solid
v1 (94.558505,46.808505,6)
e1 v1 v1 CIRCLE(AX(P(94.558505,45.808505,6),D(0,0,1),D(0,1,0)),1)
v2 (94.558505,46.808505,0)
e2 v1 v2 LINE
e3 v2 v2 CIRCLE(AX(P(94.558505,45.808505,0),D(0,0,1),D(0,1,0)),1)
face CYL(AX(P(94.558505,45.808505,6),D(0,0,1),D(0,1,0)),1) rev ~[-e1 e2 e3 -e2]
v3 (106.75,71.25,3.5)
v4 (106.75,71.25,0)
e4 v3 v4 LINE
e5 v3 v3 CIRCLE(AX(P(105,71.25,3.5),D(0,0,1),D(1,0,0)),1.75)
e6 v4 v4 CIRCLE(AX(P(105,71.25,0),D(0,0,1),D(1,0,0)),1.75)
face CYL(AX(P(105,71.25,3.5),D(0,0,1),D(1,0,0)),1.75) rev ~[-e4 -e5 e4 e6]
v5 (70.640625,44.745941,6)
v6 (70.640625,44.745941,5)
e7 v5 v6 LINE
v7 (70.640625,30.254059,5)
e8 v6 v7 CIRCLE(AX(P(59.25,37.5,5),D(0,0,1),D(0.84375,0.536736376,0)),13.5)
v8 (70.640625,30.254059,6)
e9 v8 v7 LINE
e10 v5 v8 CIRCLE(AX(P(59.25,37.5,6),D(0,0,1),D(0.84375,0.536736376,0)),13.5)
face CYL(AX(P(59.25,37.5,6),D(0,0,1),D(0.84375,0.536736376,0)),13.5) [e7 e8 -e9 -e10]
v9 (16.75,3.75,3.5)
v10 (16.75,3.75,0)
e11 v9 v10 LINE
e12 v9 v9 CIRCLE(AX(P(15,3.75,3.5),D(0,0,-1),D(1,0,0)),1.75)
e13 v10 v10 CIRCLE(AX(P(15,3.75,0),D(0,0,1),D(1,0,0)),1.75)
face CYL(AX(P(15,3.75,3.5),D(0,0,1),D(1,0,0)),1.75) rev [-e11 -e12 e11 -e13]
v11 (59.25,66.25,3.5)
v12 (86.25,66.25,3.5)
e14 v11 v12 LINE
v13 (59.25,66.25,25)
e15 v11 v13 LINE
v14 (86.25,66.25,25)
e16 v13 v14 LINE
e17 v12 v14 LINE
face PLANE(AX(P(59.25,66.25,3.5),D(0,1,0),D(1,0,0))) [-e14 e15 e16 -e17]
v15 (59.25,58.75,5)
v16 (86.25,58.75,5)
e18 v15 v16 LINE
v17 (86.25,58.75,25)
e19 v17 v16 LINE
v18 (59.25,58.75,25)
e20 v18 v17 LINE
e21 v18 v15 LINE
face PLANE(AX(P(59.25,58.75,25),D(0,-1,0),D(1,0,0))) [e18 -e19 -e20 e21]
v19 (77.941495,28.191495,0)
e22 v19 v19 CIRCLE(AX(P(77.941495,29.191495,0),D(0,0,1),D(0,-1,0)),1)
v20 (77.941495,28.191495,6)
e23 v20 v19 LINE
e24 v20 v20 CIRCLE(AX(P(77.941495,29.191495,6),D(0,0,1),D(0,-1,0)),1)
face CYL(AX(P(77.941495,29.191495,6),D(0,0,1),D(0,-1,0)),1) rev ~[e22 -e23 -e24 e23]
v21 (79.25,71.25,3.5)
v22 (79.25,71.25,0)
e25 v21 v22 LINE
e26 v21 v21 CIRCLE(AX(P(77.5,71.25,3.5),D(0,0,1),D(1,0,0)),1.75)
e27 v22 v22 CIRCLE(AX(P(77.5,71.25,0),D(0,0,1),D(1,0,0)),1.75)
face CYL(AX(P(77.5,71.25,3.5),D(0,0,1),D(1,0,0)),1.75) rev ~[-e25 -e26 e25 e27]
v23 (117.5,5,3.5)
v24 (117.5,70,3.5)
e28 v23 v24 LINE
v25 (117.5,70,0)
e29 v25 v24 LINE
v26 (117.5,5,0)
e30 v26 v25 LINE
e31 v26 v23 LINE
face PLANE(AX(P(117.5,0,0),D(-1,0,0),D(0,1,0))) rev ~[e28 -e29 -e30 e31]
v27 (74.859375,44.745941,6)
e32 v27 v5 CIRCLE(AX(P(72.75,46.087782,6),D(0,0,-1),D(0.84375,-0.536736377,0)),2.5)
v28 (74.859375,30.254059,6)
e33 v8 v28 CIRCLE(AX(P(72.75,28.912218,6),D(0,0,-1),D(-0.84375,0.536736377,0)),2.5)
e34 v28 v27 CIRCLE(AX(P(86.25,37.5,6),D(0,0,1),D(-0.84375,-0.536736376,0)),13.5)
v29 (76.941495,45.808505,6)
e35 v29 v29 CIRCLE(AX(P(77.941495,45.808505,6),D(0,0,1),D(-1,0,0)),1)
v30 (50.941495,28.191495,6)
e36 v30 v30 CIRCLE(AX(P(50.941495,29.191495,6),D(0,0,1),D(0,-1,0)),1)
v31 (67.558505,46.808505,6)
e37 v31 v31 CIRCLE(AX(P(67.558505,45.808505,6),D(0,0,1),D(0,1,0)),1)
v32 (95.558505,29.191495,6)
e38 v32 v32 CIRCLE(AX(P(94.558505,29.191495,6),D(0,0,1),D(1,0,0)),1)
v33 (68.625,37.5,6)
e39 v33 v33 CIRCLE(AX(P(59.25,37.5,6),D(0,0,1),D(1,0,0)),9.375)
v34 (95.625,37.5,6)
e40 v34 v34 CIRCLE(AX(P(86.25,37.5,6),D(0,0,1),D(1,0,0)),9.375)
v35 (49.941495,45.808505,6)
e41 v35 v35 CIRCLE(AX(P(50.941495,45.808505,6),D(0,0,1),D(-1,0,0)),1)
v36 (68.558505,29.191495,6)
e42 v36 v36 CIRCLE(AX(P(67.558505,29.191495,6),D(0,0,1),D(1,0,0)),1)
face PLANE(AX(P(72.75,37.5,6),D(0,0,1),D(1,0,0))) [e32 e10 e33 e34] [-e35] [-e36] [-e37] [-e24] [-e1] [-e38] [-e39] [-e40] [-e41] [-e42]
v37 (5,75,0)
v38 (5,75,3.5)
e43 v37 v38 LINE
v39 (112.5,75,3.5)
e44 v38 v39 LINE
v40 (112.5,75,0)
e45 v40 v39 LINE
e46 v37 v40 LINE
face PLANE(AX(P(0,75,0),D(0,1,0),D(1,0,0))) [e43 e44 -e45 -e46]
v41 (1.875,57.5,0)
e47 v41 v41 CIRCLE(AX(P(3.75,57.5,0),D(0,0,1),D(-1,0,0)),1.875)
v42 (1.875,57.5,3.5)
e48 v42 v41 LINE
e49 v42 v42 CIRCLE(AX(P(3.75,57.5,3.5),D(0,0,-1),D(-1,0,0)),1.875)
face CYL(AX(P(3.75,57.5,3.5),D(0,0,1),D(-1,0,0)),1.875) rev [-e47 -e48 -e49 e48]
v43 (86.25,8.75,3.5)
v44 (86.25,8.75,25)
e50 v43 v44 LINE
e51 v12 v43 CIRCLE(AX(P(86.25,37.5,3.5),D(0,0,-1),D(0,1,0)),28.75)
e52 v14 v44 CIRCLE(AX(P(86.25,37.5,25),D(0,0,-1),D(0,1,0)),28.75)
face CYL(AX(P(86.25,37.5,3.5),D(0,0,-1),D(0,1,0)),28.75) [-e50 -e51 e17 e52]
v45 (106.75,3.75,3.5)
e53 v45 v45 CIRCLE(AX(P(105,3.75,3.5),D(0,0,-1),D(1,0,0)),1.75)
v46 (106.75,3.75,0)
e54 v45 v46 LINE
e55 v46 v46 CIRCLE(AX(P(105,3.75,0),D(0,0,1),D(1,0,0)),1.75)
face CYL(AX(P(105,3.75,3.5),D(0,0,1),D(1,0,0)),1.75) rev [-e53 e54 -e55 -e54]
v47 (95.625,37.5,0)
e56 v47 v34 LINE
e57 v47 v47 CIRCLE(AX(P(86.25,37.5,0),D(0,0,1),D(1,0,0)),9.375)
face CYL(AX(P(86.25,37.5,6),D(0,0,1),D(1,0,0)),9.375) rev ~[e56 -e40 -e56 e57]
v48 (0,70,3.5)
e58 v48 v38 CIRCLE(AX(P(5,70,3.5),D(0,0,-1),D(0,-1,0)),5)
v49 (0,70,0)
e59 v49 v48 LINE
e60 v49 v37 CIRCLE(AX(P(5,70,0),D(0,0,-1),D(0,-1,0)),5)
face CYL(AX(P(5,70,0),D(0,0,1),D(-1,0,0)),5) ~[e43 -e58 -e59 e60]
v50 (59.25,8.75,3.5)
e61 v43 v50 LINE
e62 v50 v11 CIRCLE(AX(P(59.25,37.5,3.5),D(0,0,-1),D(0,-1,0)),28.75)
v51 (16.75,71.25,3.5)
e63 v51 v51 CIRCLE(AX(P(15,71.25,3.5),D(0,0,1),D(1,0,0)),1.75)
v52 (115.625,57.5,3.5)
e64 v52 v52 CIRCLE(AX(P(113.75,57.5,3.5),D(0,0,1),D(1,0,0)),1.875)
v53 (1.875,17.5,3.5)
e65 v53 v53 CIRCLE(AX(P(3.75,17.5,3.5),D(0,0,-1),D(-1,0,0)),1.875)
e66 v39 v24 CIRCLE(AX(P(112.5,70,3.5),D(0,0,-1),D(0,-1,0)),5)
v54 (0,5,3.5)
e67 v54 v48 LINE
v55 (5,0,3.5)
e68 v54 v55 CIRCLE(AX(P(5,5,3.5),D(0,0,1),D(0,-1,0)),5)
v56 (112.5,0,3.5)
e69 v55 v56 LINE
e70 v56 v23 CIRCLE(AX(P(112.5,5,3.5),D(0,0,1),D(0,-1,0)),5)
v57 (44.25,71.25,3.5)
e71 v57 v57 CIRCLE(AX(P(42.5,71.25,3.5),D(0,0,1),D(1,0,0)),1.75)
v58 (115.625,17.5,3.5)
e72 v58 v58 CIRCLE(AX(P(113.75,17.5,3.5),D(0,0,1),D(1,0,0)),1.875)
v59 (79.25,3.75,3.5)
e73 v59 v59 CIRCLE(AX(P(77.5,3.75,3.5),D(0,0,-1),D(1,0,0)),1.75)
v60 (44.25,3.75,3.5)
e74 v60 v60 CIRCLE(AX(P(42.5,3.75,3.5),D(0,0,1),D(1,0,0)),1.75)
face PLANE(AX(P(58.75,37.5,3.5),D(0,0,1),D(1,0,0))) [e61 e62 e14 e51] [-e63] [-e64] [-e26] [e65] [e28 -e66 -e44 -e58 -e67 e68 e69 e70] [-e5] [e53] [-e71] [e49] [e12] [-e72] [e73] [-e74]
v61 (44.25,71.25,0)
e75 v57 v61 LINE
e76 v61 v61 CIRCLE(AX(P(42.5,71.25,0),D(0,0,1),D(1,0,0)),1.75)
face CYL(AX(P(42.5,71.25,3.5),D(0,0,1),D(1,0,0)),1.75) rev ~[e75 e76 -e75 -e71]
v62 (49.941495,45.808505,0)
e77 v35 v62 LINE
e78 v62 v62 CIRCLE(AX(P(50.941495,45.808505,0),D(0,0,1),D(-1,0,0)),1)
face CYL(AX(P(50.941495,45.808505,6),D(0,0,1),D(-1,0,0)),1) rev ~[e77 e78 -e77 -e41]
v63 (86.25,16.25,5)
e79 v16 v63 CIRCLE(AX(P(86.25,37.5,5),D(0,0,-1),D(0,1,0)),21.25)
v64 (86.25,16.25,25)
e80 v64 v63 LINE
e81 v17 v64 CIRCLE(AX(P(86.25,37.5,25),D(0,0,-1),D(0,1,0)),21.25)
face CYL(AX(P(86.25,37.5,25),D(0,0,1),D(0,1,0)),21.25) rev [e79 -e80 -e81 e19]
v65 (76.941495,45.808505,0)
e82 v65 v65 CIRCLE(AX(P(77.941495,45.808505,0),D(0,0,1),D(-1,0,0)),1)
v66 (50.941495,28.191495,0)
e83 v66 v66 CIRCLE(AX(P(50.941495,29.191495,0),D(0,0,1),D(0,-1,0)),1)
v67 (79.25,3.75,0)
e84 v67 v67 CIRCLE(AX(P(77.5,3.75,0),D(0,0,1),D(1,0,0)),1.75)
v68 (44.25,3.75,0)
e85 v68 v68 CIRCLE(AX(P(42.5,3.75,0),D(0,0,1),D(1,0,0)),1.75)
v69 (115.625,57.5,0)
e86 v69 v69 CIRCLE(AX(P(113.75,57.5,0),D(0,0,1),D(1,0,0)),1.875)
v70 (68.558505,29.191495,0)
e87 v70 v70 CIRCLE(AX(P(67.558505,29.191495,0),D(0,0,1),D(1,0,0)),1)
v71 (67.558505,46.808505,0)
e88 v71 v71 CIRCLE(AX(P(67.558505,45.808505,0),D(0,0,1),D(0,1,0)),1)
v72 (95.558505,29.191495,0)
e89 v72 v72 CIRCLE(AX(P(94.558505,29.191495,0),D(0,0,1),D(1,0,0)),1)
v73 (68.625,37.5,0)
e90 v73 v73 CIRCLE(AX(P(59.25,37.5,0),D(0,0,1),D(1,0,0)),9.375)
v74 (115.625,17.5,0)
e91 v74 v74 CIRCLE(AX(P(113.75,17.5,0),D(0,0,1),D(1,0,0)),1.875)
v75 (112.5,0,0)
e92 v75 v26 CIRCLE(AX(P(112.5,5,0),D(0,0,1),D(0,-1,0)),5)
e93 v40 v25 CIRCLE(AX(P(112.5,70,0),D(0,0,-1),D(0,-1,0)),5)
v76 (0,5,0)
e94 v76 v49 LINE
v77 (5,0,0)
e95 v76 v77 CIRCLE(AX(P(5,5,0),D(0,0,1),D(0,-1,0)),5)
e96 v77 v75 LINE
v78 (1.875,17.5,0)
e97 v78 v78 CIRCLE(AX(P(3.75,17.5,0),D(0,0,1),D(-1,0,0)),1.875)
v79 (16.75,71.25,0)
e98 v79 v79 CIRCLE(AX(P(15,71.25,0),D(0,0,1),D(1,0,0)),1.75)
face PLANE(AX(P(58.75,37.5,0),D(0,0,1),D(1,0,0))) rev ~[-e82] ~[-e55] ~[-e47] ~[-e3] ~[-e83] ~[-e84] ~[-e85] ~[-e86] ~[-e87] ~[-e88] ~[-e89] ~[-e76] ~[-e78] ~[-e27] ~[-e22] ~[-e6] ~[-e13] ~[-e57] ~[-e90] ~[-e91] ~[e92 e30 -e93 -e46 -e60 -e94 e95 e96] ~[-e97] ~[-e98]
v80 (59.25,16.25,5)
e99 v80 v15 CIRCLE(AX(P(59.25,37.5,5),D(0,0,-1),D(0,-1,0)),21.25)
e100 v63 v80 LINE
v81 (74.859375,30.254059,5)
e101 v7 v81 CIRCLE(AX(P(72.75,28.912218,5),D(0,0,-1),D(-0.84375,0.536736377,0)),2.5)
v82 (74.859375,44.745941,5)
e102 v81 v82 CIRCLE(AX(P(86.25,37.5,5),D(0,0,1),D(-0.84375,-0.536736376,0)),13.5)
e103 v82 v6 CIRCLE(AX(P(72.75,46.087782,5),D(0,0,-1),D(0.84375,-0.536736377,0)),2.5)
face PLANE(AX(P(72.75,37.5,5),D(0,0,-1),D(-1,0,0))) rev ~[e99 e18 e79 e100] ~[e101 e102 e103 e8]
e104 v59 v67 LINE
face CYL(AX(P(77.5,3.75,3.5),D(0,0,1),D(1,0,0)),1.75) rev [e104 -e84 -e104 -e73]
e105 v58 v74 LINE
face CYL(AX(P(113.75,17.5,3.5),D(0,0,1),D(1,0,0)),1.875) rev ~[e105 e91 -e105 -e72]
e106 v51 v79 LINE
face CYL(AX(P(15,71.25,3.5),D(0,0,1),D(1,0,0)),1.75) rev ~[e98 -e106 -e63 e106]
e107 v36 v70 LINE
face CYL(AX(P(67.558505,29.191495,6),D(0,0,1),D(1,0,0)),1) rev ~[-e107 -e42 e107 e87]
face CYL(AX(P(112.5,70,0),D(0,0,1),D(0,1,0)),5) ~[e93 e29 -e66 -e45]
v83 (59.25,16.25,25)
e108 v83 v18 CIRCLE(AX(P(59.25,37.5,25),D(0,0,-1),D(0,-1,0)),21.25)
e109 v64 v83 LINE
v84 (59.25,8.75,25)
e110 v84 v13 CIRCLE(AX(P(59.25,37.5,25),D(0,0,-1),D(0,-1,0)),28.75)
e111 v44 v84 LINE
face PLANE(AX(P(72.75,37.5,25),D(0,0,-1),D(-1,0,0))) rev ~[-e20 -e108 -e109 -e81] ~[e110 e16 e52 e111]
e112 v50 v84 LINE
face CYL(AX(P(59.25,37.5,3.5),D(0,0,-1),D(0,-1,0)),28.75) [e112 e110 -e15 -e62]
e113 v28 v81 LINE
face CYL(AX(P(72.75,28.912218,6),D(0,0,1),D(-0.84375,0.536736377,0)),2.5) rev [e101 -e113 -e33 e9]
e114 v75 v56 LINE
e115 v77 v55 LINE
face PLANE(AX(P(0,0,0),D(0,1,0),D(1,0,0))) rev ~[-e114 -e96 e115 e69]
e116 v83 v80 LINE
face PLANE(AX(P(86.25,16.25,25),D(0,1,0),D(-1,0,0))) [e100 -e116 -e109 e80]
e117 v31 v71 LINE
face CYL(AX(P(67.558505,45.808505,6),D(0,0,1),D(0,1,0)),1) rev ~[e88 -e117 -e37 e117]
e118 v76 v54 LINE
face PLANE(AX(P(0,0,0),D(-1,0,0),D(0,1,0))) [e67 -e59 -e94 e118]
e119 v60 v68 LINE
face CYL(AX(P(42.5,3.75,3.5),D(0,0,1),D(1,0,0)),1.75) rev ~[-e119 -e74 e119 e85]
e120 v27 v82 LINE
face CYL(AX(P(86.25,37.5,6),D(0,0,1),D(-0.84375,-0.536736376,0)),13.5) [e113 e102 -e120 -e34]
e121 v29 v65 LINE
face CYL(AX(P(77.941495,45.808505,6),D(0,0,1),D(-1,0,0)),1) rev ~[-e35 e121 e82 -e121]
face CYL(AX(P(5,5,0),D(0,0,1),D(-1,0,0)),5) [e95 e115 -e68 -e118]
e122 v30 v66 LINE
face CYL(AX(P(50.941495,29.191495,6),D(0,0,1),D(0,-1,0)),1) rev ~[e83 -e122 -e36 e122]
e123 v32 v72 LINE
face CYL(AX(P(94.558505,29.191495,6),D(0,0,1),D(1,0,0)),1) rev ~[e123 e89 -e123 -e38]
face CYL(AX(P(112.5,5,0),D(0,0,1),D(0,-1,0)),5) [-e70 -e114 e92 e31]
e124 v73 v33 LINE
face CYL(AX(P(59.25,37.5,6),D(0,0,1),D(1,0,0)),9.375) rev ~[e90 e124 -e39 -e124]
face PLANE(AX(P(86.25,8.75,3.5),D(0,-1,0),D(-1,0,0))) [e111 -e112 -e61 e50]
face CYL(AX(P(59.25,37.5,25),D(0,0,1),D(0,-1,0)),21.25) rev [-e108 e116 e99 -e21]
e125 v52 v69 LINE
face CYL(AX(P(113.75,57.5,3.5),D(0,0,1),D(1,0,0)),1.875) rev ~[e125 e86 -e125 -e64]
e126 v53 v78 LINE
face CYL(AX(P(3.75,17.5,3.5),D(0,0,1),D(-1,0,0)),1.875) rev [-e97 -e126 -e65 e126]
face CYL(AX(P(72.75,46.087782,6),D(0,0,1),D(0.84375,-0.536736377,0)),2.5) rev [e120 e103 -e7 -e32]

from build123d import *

# Parameters (mm, degrees)
FLANGE_PLATE_SKETCH_W              = 117.5
FLANGE_PLATE_SKETCH_H              = 75
FLANGE_PLATE_DEPTH                 = 3.5
HOUSING_WALL_DEPTH                 = 21.5
HOUSING_CAVITY_DEPTH               = 20
DUAL_BORE_SKETCH_R                 = 9.375
DUAL_BORES_DEPTH                   = 141.823471055
BORE_START                         = 1
BORE_PAD_SKETCH_R                  = 9.375
BORE_PADS_DEPTH                    = 1
BORE_SLOT_SKETCH_R                 = 1
BORE_SLOT_CUT_DEPTH                = 141.684931674
BORE_SLOT_PATTERN_4X_COUNT         = 4
BORE_NOTCH_SKETCH_R                = 1
BORE_NOTCH_CUT_DEPTH               = 141.684931674
BORE_NOTCH_PATTERN_4X_COUNT        = 4
FLANGE_CORNER_FILLETS_R5_R         = 5
FLANGE_EDGE_HOLE_SKETCH_R          = 1.75
FLANGE_EDGE_HOLE_DEPTH             = 142.044319276
FLANGE_EDGE_HOLE_PATTERN_COUNT     = 2
FLANGE_EDGE_HOLE_PATTERN_PITCH     = 27.5
FLANGE_SIDE_HOLE_SKETCH_R          = 1.75
FLANGE_SIDE_HOLES_DEPTH            = 142.044319276
FLANGE_CORNER_HOLE_SKETCH_R        = 1.875
FLANGE_CORNER_HOLES_DEPTH          = 142.044319276
FLANGE_HOLE_MIRROR_COPY_1_SKETCH_R = 1.75
FLANGE_HOLE_MIRROR_COPY_1_DEPTH    = 142.044319276


with BuildPart() as part:
    # Flange Plate Sketch → Flange Plate (new body)
    with BuildSketch(Plane.XY):
        with Locations((58.75, 37.5)):
            Rectangle(FLANGE_PLATE_SKETCH_W, FLANGE_PLATE_SKETCH_H)
    extrude(amount=FLANGE_PLATE_DEPTH)

    # Housing Wall Sketch → Housing Wall (add)
    with BuildSketch(Plane.XY.offset(3.5)):
        with BuildLine():
            Line((59.25, 66.25), (86.25, 66.25))
            ThreePointArc((86.25, 66.25), (115, 37.5), (86.25, 8.75))
            Line((86.25, 8.75), (59.25, 8.75))
            ThreePointArc((59.25, 8.75), (30.5, 37.5), (59.25, 66.25))
        make_face()
    extrude(amount=HOUSING_WALL_DEPTH)

    # Housing Cavity Sketch → Housing Cavity (cut)
    with BuildSketch(Plane.XY.offset(25)):
        with BuildLine():
            Line((86.25, 16.25), (59.25, 16.25))
            ThreePointArc((59.25, 16.25), (38, 37.5), (59.25, 58.75))
            Line((59.25, 58.75), (86.25, 58.75))
            ThreePointArc((86.25, 58.75), (107.5, 37.5), (86.25, 16.25))
        make_face()
    extrude(amount=-HOUSING_CAVITY_DEPTH, mode=Mode.SUBTRACT)

    # Dual Bore Sketch → Dual Bores (cut, through all)
    with BuildSketch(Plane.XY.offset(5)):
        with Locations((59.25, 37.5)):
            Circle(DUAL_BORE_SKETCH_R)
        with Locations((86.25, 37.5)):
            Circle(DUAL_BORE_SKETCH_R)
    extrude(amount=-DUAL_BORES_DEPTH, mode=Mode.SUBTRACT)

    # Bore Pad Sketch → Bore Pads (add)
    with BuildSketch(Plane.XY.offset(5).offset(BORE_START)):
        with BuildLine():
            ThreePointArc((70.640625, 44.745941078), (45.75, 37.5), (70.640625, 30.254058922))
            ThreePointArc((70.640625, 30.254058922), (72.75, 31.412217981), (74.859375, 30.254058922))
            ThreePointArc((74.859375, 30.254058922), (99.75, 37.5), (74.859375, 44.745941078))
            ThreePointArc((74.859375, 44.745941078), (72.75, 43.587782019), (70.640625, 44.745941078))
        make_face()
        with Locations((59.25, 37.5)):
            Circle(BORE_PAD_SKETCH_R, mode=Mode.SUBTRACT)
        with Locations((86.25, 37.5)):
            Circle(BORE_PAD_SKETCH_R, mode=Mode.SUBTRACT)
    extrude(amount=-BORE_PADS_DEPTH)

    # Bore Slot Sketch → Bore Slot Cut (cut, through all)
    with BuildSketch(Plane.XY.offset(6)):
        with Locations((67.558504679, 29.191495321)):
            Circle(BORE_SLOT_SKETCH_R)
    bore_slot_cut = extrude(amount=-BORE_SLOT_CUT_DEPTH, mode=Mode.SUBTRACT)

    # Bore Slot Pattern 4x: Bore Slot Cut ×4 about axis
    bore_slot_pattern_4x_axis = Axis((59.25, 37.5, 0), (0, 0, 1))
    for i in range(1, BORE_SLOT_PATTERN_4X_COUNT):
        add(bore_slot_cut.rotate(bore_slot_pattern_4x_axis, i * 360 / BORE_SLOT_PATTERN_4X_COUNT), mode=Mode.SUBTRACT)

    # Bore Notch Sketch → Bore Notch Cut (cut, through all)
    with BuildSketch(Plane.XY.offset(6)):
        with Locations((94.558504679, 29.191495321)):
            Circle(BORE_NOTCH_SKETCH_R)
    bore_notch_cut = extrude(amount=-BORE_NOTCH_CUT_DEPTH, mode=Mode.SUBTRACT)

    # Bore Notch Pattern 4x: Bore Notch Cut ×4 about axis
    bore_notch_pattern_4x_axis = Axis((86.25, 37.5, 0), (0, 0, 1))
    for i in range(1, BORE_NOTCH_PATTERN_4X_COUNT):
        add(bore_notch_cut.rotate(bore_notch_pattern_4x_axis, i * 360 / BORE_NOTCH_PATTERN_4X_COUNT), mode=Mode.SUBTRACT)

    # Flange Corner Fillets R5
    flange_corner_fillets_r5_edges = [part.edges().sort_by_distance(p)[0] for p in [
        (0, 75, 1.75),
        (117.5, 75, 1.75),
        (117.5, 0, 1.75),
        (0, 0, 1.75),
    ]]
    fillet(flange_corner_fillets_r5_edges, radius=FLANGE_CORNER_FILLETS_R5_R)

    # Flange Edge Hole Sketch → Flange Edge Hole (cut, through all)
    with BuildSketch(Plane.XY.offset(3.5)):
        with Locations((15, 71.25)):
            Circle(FLANGE_EDGE_HOLE_SKETCH_R)
    flange_edge_hole = extrude(amount=-FLANGE_EDGE_HOLE_DEPTH, mode=Mode.SUBTRACT)

    # Flange Edge Hole Pattern: Flange Edge Hole ×2
    with Locations(*[(i * FLANGE_EDGE_HOLE_PATTERN_PITCH, 0, 0) for i in range(1, FLANGE_EDGE_HOLE_PATTERN_COUNT)]):
        add(flange_edge_hole, mode=Mode.SUBTRACT)

    # Flange Side Hole Sketch → Flange Side Holes (cut, through all)
    with BuildSketch(Plane.XY.offset(3.5)):
        with Locations((77.5, 71.25)):
            Circle(FLANGE_SIDE_HOLE_SKETCH_R)
        with Locations((105, 71.25)):
            Circle(FLANGE_SIDE_HOLE_SKETCH_R)
    flange_side_holes = extrude(amount=-FLANGE_SIDE_HOLES_DEPTH, mode=Mode.SUBTRACT)

    # Flange Corner Hole Sketch → Flange Corner Holes (cut, through all)
    with BuildSketch(Plane.XY.offset(3.5)):
        with Locations((113.75, 57.5)):
            Circle(FLANGE_CORNER_HOLE_SKETCH_R)
        with Locations((113.75, 17.5)):
            Circle(FLANGE_CORNER_HOLE_SKETCH_R)
    flange_corner_holes = extrude(amount=-FLANGE_CORNER_HOLES_DEPTH, mode=Mode.SUBTRACT)

    # Flange Hole Mirror: Flange Edge Hole, Flange Side Holes across plane
    add(flange_edge_hole.mirror(Plane.ZX.offset(37.5)), mode=Mode.SUBTRACT)
    add(flange_side_holes.mirror(Plane.ZX.offset(37.5)), mode=Mode.SUBTRACT)

    # Flange Hole Mirror copy 1 sketch → Flange Hole Mirror copy 1 (cut, through all)
    with BuildSketch(Plane(origin=(27.5, 75, 3.5), x_dir=(1, 0, 0), z_dir=(0, 0, 1))):
        with Locations((15, -71.25)):
            Circle(FLANGE_HOLE_MIRROR_COPY_1_SKETCH_R)
    extrude(amount=-FLANGE_HOLE_MIRROR_COPY_1_DEPTH, mode=Mode.SUBTRACT)

    # Corner Hole Mirror: Flange Corner Holes across plane
    add(flange_corner_holes.mirror(Plane(origin=(58.75, 0, 0), x_dir=(0, 0, 1), z_dir=(1, 0, 0))), mode=Mode.SUBTRACT)


solid = part.part
